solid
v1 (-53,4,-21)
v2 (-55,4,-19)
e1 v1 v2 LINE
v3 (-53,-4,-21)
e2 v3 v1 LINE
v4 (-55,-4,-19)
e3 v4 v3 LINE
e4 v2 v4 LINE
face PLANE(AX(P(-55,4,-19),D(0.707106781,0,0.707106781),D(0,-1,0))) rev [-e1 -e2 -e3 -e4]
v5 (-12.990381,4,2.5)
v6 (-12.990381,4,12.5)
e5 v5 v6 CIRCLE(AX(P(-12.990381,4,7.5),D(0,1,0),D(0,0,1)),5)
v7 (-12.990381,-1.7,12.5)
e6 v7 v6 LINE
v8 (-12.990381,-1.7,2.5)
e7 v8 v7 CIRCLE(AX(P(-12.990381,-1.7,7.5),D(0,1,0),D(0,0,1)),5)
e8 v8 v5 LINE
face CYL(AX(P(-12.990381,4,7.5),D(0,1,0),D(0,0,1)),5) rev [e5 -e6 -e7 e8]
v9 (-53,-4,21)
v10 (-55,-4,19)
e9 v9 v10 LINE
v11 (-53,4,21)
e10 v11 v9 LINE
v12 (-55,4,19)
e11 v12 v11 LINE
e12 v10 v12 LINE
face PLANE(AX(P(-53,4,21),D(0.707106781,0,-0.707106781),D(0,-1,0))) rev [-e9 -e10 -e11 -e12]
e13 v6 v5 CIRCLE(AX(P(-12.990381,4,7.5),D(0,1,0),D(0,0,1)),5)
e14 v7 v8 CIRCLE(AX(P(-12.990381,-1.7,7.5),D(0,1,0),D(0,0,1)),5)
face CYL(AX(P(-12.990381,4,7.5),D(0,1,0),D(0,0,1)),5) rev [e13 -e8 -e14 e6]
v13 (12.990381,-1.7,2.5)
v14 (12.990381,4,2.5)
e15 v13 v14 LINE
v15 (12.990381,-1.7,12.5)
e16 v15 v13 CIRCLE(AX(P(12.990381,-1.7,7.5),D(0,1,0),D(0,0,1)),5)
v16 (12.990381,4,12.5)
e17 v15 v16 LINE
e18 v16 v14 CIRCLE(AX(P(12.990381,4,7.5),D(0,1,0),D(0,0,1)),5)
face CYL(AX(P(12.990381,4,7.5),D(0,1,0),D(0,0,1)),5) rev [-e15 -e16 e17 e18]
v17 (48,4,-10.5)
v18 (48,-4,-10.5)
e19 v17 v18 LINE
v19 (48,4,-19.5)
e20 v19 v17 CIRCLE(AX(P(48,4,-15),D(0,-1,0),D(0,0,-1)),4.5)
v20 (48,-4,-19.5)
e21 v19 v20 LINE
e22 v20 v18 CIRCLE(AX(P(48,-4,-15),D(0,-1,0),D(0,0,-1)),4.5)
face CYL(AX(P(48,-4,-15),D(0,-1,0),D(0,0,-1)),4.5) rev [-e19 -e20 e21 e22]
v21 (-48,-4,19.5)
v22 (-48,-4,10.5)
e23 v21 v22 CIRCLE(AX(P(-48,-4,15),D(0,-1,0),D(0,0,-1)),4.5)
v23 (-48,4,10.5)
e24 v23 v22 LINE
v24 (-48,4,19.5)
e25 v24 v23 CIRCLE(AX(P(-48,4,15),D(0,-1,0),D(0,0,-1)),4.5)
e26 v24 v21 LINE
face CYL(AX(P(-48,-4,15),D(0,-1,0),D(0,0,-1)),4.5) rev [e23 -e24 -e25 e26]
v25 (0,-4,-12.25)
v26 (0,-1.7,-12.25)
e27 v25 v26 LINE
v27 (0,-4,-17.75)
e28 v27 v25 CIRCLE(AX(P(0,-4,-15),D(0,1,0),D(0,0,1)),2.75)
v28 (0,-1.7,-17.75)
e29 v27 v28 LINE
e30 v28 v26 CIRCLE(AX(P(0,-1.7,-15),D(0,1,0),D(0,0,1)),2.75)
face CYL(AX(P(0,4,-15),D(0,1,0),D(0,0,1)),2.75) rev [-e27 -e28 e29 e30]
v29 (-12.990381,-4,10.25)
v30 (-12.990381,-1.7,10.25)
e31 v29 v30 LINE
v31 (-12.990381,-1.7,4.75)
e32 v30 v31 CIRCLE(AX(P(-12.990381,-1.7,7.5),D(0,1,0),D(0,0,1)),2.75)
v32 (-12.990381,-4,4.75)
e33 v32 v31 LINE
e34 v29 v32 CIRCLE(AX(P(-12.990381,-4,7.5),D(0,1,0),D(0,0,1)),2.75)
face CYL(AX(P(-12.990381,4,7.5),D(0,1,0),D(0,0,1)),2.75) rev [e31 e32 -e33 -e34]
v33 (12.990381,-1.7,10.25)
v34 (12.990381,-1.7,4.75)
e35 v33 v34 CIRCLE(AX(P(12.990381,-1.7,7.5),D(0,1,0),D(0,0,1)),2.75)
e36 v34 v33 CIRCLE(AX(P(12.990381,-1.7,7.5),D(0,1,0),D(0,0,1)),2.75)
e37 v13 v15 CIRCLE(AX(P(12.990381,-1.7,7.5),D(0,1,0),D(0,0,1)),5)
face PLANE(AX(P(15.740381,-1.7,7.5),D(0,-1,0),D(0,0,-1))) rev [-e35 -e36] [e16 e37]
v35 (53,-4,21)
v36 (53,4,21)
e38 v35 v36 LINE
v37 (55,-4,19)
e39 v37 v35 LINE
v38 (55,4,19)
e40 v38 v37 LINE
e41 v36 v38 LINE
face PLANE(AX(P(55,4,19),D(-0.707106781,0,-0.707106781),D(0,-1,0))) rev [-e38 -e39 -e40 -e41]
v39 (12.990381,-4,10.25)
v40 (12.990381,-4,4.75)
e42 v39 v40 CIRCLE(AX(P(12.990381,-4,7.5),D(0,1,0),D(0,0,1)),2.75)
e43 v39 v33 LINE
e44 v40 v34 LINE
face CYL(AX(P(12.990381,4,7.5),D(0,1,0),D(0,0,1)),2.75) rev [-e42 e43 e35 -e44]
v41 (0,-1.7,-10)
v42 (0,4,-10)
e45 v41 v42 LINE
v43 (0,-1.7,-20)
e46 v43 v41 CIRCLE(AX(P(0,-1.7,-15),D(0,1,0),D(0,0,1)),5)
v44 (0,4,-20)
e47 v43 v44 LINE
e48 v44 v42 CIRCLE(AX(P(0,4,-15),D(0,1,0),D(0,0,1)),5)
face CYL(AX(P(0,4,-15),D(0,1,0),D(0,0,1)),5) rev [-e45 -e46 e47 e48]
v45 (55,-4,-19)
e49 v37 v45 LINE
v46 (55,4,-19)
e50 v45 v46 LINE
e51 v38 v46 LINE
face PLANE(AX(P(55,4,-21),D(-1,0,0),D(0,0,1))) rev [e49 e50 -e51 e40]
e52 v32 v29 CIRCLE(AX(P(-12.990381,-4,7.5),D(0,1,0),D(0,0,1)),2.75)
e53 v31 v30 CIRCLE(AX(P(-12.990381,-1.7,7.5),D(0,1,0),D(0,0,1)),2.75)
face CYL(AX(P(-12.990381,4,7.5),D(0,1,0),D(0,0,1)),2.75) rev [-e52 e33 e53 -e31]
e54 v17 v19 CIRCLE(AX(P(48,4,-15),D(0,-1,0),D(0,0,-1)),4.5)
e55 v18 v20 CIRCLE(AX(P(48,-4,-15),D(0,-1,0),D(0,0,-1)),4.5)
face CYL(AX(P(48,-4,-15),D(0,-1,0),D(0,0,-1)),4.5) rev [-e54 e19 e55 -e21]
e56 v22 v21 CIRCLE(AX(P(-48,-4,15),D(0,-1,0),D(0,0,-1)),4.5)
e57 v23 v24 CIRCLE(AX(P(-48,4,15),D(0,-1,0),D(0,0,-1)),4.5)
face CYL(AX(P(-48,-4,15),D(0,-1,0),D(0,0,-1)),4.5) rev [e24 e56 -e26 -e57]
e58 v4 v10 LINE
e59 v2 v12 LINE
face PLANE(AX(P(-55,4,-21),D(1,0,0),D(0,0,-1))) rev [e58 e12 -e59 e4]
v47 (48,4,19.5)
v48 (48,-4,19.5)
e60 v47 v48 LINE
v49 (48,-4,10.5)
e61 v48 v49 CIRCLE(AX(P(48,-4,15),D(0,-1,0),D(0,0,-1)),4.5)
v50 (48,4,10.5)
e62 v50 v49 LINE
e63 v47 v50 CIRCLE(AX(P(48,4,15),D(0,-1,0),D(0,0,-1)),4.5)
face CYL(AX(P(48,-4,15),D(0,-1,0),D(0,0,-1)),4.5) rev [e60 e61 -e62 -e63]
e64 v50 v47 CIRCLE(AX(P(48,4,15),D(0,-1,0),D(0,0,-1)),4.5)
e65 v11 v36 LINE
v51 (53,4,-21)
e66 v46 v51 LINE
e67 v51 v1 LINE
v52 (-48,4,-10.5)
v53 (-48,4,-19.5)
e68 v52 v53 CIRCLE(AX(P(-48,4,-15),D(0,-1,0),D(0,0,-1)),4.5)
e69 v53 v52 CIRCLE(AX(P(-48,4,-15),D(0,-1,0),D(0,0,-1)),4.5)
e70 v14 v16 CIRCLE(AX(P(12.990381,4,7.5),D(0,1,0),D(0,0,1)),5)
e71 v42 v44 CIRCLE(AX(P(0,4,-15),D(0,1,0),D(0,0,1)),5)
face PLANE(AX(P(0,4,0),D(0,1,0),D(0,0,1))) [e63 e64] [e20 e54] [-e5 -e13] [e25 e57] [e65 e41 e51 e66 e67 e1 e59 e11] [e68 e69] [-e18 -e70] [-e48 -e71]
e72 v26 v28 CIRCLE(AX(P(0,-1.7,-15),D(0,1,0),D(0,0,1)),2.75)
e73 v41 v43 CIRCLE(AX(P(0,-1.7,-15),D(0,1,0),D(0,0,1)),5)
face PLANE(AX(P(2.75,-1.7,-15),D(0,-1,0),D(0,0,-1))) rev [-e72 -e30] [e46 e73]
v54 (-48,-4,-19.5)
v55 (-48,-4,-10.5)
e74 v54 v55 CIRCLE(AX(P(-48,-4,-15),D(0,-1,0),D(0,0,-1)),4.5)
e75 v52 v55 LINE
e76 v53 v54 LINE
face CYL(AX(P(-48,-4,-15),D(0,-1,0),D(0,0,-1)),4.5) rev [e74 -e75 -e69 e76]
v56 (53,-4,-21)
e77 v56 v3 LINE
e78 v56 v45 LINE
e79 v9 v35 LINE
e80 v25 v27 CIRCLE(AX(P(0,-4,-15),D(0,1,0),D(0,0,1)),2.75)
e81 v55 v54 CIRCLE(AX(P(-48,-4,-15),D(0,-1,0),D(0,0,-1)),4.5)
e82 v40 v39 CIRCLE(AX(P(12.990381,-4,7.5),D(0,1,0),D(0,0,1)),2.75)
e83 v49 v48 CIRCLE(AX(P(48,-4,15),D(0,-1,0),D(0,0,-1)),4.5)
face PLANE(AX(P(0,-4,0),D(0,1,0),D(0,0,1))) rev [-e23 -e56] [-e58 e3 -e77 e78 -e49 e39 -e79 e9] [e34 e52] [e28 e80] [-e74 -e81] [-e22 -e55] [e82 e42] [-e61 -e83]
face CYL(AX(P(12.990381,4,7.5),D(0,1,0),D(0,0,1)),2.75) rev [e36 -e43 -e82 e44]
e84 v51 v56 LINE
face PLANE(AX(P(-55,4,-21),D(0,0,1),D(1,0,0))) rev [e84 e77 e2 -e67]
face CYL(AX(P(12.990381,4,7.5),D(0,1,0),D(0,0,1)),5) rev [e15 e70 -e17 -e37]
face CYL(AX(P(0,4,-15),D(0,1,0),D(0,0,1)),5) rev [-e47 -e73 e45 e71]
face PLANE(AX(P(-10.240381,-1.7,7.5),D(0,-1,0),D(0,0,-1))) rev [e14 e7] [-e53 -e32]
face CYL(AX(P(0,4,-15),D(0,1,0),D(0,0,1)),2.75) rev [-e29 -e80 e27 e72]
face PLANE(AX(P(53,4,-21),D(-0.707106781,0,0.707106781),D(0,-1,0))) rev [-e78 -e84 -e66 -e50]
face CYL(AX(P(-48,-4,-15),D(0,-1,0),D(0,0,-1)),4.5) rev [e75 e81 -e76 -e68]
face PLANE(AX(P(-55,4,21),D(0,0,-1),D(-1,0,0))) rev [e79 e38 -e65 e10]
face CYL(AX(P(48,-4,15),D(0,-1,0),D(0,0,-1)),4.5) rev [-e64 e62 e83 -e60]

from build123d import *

# Parameters (mm, degrees)
SKETCH_1_W                   = 110
SKETCH_1_H                   = 42
EXTRUDE_1_DEPTH              = 4
HOLE_WIZARD_M6_1_D           = 5.5
HOLE_WIZARD_M6_1_CBORE_D     = 10
HOLE_WIZARD_M6_1_CBORE_DEPTH = 5.7
HOLE_WIZARD_9_0_9_1_D        = 9
CHAMFER_1_SIZE               = 2
MIRROR_2_COPY_1_D            = 9


with BuildPart() as part:
    # 草图1 → 凸台-拉伸1 (new, symmetric)
    with BuildSketch(Plane(origin=(0, 0, 0), x_dir=(1, 0, 0), z_dir=(0, 1, 0))):
        Rectangle(SKETCH_1_W, SKETCH_1_H)
    extrude(amount=EXTRUDE_1_DEPTH, both=True)

    # M6 六角凹头螺钉的柱形沉头孔1 (through all)
    with Locations(Plane(origin=(0, 4, 0), x_dir=(1, 0, 0), z_dir=(0, 1, 0))):
        with Locations((0, 15), (-12.990381057, -7.5), (12.990381057, -7.5)):
            CounterBoreHole(HOLE_WIZARD_M6_1_D / 2, HOLE_WIZARD_M6_1_CBORE_D / 2, HOLE_WIZARD_M6_1_CBORE_DEPTH)

    # Ø9.0 (9) 直径孔1 (through all)
    with Locations(Plane(origin=(0, -4, 0), x_dir=(-1, 0, 0), z_dir=(0, -1, 0))):
        with Locations((-48, -15)):
            hole_wizard_9_0_9_1 = Hole(HOLE_WIZARD_9_0_9_1_D / 2)

    # 倒角1
    chamfer_1_edges = [part.edges().sort_by_distance(p)[0] for p in [
        (55, 0, 21),
        (-55, 0, 21),
        (-55, 0, -21),
        (55, 0, -21),
    ]]
    chamfer(chamfer_1_edges, length=CHAMFER_1_SIZE)

    # 镜向1: Ø9.0 (9) 直径孔1 across plane
    add(hole_wizard_9_0_9_1.mirror(Plane.XY), mode=Mode.SUBTRACT)

    # 镜向2: Ø9.0 (9) 直径孔1 across plane
    add(hole_wizard_9_0_9_1.mirror(Plane(origin=(0, 0, 0), x_dir=(0, 0, 1), z_dir=(1, 0, 0))), mode=Mode.SUBTRACT)

    # 镜向2 copy 1 (through all)
    with Locations(Plane.XZ.offset(4)):
        with Locations((-48, -15)):
            Hole(MIRROR_2_COPY_1_D / 2)


solid = part.part
